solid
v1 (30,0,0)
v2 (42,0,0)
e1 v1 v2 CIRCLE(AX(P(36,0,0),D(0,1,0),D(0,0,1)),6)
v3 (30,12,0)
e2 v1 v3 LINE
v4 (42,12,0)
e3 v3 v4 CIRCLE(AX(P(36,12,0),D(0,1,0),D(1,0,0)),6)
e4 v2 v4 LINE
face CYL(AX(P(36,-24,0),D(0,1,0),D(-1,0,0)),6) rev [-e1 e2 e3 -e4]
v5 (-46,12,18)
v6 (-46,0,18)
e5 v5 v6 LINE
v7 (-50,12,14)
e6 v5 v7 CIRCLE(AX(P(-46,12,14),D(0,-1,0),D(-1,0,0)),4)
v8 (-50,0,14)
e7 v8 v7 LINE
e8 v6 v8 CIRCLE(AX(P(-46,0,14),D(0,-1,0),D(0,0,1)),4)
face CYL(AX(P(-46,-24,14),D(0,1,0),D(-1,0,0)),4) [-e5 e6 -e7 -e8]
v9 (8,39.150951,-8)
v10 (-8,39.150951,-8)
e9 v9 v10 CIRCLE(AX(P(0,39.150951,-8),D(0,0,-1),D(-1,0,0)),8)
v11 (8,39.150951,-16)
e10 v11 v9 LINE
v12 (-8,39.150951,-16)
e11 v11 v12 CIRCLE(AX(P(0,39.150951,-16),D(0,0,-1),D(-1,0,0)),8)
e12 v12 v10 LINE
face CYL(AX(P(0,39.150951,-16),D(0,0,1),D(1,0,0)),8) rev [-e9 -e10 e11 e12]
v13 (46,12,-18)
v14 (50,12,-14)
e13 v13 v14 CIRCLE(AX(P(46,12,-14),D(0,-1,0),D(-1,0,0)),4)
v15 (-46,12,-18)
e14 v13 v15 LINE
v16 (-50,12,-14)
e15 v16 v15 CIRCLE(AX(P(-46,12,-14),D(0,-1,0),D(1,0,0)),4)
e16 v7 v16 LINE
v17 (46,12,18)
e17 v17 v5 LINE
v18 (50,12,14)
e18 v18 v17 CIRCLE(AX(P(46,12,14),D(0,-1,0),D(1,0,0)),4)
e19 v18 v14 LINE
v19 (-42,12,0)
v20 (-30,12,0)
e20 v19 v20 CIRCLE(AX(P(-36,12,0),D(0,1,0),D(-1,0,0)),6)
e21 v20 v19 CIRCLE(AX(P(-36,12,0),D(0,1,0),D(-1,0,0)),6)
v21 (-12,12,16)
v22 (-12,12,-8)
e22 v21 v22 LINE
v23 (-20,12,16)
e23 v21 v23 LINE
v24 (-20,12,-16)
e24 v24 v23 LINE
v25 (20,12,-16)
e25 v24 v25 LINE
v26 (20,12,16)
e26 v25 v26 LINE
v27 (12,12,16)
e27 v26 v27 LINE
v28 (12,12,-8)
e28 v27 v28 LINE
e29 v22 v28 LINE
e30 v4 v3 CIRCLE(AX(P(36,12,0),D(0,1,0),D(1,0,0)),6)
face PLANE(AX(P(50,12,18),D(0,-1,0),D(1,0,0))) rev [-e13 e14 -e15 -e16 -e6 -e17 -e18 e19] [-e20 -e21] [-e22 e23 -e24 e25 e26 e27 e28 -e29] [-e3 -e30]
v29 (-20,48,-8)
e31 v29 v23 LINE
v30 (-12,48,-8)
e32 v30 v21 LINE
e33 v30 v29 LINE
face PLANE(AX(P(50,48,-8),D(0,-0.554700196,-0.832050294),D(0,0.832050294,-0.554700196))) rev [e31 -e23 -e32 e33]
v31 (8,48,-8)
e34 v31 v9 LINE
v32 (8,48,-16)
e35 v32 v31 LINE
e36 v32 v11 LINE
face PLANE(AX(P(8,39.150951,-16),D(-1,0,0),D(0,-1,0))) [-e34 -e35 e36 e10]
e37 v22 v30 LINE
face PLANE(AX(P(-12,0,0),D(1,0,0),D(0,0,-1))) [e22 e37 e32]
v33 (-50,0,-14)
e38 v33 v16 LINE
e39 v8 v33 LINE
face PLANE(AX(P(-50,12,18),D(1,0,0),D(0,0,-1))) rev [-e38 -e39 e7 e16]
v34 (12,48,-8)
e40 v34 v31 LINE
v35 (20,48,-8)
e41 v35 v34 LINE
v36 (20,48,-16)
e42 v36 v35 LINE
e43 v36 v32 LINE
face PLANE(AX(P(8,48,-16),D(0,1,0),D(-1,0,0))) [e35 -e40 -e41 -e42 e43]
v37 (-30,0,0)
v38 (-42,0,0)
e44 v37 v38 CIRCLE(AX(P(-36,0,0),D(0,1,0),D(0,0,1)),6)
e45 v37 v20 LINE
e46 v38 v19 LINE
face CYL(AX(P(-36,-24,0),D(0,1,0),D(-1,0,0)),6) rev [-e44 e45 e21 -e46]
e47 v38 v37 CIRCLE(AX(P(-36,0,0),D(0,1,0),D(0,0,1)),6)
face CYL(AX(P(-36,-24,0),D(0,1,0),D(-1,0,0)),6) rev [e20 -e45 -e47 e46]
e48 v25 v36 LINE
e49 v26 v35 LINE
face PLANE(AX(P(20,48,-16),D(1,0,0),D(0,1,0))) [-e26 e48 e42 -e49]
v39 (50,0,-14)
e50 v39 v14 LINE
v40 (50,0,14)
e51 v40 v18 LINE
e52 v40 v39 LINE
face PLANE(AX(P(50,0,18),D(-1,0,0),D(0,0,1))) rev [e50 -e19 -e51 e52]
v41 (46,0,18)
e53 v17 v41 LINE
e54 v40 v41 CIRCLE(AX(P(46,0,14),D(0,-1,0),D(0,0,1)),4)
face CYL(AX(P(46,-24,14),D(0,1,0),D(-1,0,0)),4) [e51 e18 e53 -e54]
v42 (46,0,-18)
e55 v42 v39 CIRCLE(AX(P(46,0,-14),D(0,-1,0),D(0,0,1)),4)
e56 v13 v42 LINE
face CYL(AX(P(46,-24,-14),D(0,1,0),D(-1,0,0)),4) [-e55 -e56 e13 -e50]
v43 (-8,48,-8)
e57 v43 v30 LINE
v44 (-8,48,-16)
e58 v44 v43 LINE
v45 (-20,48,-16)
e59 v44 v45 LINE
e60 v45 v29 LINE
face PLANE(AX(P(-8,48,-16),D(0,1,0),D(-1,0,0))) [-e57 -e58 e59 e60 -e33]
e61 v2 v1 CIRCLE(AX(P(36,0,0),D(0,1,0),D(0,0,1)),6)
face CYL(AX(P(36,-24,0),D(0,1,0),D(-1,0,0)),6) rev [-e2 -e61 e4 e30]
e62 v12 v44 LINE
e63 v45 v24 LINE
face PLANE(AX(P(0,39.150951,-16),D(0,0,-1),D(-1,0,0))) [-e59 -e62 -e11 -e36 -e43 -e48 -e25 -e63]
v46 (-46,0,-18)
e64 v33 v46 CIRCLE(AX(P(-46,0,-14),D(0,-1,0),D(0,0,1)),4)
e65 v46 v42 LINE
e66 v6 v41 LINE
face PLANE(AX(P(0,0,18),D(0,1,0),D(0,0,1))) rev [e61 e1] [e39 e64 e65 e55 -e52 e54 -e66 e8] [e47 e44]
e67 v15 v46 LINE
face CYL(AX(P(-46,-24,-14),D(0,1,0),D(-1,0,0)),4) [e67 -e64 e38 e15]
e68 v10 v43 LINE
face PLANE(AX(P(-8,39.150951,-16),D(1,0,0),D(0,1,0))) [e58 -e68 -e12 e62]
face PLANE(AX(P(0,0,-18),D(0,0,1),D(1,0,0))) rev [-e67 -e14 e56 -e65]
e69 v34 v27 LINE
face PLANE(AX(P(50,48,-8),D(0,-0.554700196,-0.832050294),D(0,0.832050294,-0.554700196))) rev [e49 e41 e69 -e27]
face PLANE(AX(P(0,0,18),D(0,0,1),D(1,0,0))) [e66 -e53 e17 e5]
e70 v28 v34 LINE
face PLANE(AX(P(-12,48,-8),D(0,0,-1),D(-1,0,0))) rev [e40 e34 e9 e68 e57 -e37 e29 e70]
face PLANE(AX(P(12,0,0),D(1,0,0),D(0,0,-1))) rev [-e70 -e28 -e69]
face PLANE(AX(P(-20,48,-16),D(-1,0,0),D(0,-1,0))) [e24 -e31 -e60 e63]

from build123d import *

# Parameters (mm, degrees)
BASE_PLATE_DEPTH                      = 18
BASE_CORNERS_AND_MOUNTING_HOLES_DEPTH = 36
BASE_RELIEF_SKETCH_R                  = 6
BASE_RELIEF_CUT_DEPTH                 = 36
SUPPORT_UPRIGHT_DEPTH                 = 34
UPRIGHT_TAPER_CUT_DEPTH               = 87.764047854
BEARING_SEAT_CUT_DEPTH                = 12


with BuildPart() as part:
    # Base Plate Profile → Base Plate (new, symmetric)
    with BuildSketch(Plane.XY):
        Polygon((0, 0), (50, 0), (50, 12), (-50, 12), (-50, 0), align=None)
    extrude(amount=BASE_PLATE_DEPTH, both=True)

    # Base Corners and Holes Sketch → Base Corners and Mounting Holes (cut)
    with BuildSketch(Plane(origin=(0, 12, 0), x_dir=(1, 0, 0), z_dir=(0, 1, 0))):
        with BuildLine():
            Line((-50, -14), (-50, -18))
            Line((-50, -18), (-46, -18))
            ThreePointArc((-46, -18), (-48.828427125, -16.828427125), (-50, -14))
        make_face()
        with BuildLine():
            Line((50, -14), (50, -18))
            Line((50, -18), (46, -18))
            ThreePointArc((46, -18), (48.828427125, -16.828427125), (50, -14))
        make_face()
        with BuildLine():
            Line((50, 14), (50, 18))
            Line((50, 18), (46, 18))
            ThreePointArc((46, 18), (48.828427125, 16.828427125), (50, 14))
        make_face()
        with BuildLine():
            Line((-50, 18), (-46, 18))
            ThreePointArc((-46, 18), (-48.828427125, 16.828427125), (-50, 14))
            Line((-50, 14), (-50, 18))
        make_face()
    extrude(amount=-BASE_CORNERS_AND_MOUNTING_HOLES_DEPTH, mode=Mode.SUBTRACT)

    # Base Relief Sketch → Base Relief Cut (cut)
    with BuildSketch(Plane(origin=(0, 12, 0), x_dir=(1, 0, 0), z_dir=(0, 1, 0))):
        with Locations(Location((-36, 0, 0), (0, 0, 180))):
            Circle(BASE_RELIEF_SKETCH_R)
        with Locations(Location((36, 0, 0), (0, 0, 270))):
            Circle(BASE_RELIEF_SKETCH_R)
    extrude(amount=-BASE_RELIEF_CUT_DEPTH, mode=Mode.SUBTRACT)

    # Upright Profile → Support Upright (add)
    with BuildSketch(Plane.XY.offset(18)):
        with BuildLine():
            Line((8, 39.150951317), (8, 48))
            Line((8, 48), (20, 48))
            Line((20, 48), (20, 12))
            Line((20, 12), (-20, 12))
            Line((-20, 12), (-20, 48))
            Line((-20, 48), (-8, 48))
            Line((-8, 48), (-8, 39.150951317))
            ThreePointArc((-8, 39.150951317), (0, 31.150951317), (8, 39.150951317))
        make_face()
    extrude(amount=-SUPPORT_UPRIGHT_DEPTH)

    # Upright Taper Sketch → Upright Taper Cut (cut, through all)
    with BuildSketch(Plane.ZY.offset(20)):
        Polygon((-8, 48), (18, 48), (18, 12), (16, 12), align=None)
    extrude(amount=-UPRIGHT_TAPER_CUT_DEPTH, mode=Mode.SUBTRACT)

    # Bearing Seat Sketch → Bearing Seat Cut (cut, symmetric)
    with BuildSketch(Plane(origin=(0, 0, 0), x_dir=(0, 0, -1), z_dir=(1, 0, 0))):
        Polygon((8, 48), (8, 12), (-16, 12), align=None)
    extrude(amount=BEARING_SEAT_CUT_DEPTH, both=True, mode=Mode.SUBTRACT)


solid = part.part
